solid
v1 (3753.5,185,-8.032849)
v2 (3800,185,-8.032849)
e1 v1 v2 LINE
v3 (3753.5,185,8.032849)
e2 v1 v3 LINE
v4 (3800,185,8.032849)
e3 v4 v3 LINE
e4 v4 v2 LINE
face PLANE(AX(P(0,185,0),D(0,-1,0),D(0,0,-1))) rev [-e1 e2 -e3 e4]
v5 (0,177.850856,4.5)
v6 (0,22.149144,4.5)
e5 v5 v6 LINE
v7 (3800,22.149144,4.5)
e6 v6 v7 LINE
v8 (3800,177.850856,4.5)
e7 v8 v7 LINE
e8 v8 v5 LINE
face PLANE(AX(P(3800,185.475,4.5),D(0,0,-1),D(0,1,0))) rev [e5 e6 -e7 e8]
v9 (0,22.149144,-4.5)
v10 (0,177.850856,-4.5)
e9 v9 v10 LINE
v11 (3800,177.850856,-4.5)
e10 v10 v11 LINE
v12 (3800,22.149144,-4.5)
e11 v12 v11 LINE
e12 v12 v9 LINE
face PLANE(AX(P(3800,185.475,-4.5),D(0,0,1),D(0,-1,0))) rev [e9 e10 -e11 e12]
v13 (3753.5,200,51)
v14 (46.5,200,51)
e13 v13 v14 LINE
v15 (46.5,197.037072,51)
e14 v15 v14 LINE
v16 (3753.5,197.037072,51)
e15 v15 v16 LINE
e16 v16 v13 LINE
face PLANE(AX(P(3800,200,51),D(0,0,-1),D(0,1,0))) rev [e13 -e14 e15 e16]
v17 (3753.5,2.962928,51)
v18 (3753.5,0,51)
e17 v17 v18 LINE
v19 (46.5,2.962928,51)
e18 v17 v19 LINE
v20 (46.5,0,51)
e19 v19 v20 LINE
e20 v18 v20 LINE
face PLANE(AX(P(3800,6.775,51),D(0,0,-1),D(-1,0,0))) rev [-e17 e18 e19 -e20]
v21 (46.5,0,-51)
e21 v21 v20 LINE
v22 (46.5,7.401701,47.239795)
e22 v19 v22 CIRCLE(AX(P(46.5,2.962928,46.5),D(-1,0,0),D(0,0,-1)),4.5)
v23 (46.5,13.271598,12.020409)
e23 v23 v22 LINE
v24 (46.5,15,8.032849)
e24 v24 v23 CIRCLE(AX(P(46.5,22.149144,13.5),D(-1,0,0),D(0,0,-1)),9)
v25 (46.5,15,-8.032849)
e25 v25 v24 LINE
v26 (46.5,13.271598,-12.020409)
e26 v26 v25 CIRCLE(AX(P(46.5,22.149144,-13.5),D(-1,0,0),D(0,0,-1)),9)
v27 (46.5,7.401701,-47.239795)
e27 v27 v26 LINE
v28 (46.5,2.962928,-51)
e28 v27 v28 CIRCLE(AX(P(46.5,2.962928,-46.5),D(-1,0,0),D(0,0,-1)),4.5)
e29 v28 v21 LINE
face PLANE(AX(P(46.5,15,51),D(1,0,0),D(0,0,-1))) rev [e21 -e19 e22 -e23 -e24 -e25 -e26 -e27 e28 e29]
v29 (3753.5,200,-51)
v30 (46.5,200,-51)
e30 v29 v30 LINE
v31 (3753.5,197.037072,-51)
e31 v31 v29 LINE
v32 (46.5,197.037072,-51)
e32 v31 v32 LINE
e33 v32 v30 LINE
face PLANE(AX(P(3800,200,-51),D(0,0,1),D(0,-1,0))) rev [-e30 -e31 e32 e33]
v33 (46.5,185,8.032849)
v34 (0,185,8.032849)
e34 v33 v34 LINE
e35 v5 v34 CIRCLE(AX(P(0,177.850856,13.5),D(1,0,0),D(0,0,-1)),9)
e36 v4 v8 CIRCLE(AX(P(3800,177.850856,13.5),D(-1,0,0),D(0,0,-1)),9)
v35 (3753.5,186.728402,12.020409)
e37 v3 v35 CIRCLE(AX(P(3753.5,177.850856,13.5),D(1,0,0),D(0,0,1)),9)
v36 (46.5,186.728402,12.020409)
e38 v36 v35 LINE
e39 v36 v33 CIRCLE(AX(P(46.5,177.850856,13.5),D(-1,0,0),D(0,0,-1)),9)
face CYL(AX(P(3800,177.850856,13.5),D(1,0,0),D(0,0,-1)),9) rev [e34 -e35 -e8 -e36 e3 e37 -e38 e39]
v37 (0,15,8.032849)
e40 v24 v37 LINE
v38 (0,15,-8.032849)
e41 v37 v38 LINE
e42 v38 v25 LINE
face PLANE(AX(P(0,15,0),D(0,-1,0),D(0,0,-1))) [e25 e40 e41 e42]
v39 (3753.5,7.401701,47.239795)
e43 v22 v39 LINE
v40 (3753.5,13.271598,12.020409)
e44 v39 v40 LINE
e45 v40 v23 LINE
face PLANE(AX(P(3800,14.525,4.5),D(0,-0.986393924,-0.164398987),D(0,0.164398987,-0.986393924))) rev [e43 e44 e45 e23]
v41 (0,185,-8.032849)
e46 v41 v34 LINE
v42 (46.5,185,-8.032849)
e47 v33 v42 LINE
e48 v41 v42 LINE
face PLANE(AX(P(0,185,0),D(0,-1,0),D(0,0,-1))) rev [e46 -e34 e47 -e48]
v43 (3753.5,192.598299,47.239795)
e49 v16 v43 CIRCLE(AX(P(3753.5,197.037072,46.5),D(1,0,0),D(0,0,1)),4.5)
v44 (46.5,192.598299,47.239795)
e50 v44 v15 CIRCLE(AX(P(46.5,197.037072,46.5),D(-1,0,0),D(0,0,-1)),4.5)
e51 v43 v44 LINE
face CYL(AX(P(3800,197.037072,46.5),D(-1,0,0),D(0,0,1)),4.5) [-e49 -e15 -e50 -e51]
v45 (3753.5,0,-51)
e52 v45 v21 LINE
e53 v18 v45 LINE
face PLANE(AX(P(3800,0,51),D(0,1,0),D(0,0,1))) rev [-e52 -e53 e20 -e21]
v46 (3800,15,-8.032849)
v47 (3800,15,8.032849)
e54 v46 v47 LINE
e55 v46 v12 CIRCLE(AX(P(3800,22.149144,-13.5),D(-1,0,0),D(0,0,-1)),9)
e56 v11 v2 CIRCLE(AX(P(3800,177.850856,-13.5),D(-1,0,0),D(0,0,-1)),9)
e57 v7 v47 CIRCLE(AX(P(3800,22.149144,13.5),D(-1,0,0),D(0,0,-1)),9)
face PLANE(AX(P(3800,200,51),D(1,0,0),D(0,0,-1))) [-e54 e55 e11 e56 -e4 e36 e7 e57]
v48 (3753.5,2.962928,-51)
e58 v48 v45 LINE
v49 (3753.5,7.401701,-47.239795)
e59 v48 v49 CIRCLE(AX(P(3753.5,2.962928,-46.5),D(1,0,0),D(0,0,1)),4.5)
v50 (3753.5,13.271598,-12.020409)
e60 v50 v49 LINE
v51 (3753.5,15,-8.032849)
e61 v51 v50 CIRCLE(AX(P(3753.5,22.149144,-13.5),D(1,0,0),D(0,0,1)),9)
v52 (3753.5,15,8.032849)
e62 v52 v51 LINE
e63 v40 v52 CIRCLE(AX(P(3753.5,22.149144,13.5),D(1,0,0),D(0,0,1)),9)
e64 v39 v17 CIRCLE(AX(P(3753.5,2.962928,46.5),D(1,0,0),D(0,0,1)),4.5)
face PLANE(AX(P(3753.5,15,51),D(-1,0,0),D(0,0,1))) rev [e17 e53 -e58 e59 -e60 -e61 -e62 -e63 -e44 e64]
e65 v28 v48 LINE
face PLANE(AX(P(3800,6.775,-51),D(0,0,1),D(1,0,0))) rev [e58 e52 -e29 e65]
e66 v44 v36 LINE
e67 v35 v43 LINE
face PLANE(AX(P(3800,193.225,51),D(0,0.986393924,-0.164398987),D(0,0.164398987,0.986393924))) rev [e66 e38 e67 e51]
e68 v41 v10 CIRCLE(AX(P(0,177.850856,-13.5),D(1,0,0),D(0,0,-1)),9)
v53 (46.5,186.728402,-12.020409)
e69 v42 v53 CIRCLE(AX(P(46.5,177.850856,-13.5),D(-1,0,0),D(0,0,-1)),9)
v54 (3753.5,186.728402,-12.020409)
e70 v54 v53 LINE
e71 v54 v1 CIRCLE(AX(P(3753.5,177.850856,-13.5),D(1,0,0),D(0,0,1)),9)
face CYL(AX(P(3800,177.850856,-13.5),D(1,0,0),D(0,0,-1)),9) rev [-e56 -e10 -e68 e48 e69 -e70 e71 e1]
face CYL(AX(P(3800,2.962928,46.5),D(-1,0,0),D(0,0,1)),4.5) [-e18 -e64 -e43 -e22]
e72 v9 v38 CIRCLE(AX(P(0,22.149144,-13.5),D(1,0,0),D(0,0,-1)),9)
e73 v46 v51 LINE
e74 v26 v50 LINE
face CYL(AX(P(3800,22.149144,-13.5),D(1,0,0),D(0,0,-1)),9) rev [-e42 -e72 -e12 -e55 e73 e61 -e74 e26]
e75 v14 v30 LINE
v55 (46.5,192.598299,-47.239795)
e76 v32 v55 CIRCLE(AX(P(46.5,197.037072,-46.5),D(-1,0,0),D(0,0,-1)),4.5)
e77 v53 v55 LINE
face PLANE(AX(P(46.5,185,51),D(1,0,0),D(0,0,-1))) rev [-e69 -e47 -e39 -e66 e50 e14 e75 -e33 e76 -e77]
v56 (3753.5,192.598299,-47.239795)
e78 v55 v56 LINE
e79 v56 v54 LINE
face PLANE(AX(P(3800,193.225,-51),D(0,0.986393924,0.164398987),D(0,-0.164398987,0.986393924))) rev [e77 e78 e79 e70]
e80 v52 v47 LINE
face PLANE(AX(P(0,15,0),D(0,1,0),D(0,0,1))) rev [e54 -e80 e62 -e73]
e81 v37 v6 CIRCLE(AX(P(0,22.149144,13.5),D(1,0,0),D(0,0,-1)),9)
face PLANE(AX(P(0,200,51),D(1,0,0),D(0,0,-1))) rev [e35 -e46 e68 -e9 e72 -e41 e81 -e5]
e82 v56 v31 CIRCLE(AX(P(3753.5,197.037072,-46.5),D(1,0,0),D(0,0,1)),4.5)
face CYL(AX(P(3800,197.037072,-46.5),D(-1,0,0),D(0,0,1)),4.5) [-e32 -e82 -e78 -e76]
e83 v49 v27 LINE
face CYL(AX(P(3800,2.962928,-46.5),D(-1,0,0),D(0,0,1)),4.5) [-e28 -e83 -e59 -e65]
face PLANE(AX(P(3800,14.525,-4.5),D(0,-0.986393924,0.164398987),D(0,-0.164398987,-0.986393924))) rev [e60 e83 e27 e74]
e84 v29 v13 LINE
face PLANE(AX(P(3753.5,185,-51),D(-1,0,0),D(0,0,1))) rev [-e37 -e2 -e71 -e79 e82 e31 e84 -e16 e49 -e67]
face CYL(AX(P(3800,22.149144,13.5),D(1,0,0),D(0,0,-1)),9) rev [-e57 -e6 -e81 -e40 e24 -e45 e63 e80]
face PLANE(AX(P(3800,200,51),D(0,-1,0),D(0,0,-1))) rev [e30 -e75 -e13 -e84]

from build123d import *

# Parameters (mm, degrees)
BASE_DEPTH         = 3800
FILLET1_R          = 9
FILLET2_R          = 4.5
SKETCH_1_W         = 46.5
SKETCH_1_H         = 102
CUT_EXTRUDE1_DEPTH = 15
SKETCH2_W          = 46.5
SKETCH2_H          = 102
CUT_EXTRUDE2_DEPTH = 15


with BuildPart() as part:
    # Sketch1 → Base (new body)
    with BuildSketch(Plane(origin=(0, 0, 0), x_dir=(0, 0, -1), z_dir=(1, 0, 0))):
        Polygon((-51, 0), (51, 0), (51, 6.775), (4.5, 14.525), (4.5, 185.475), (51, 193.225), (51, 200), (-51, 200), (-51, 193.225), (-4.5, 185.475), (-4.5, 14.525), (-51, 6.775), align=None)
    extrude(amount=BASE_DEPTH)

    # Fillet1
    fillet1_edges = [part.edges().sort_by_distance(p)[0] for p in [
        (1900, 14.525, 4.5),
        (1900, 185.475, 4.5),
        (1900, 185.475, -4.5),
        (1900, 14.525, -4.5),
    ]]
    fillet(fillet1_edges, radius=FILLET1_R)

    # Fillet2
    fillet2_edges = [part.edges().sort_by_distance(p)[0] for p in [
        (1900, 6.775, 51),
        (1900, 193.225, 51),
        (1900, 193.225, -51),
        (1900, 6.775, -51),
    ]]
    fillet(fillet2_edges, radius=FILLET2_R)

    # 草图1 → Cut-Extrude1 (cut)
    with BuildSketch(Plane(origin=(0, 200, 0), x_dir=(1, 0, 0), z_dir=(0, 1, 0))):
        with Locations((23.25, 0)):
            Rectangle(SKETCH_1_W, SKETCH_1_H)
        with Locations((3776.75, 0)):
            Rectangle(SKETCH_1_W, SKETCH_1_H)
    extrude(amount=-CUT_EXTRUDE1_DEPTH, mode=Mode.SUBTRACT)

    # Sketch2 → Cut-Extrude2 (cut)
    with BuildSketch(Plane(origin=(0, 0, 0), x_dir=(-1, 0, 0), z_dir=(0, -1, 0))):
        with Locations((-23.25, 0)):
            Rectangle(SKETCH2_W, SKETCH2_H)
        with Locations((-3776.75, 0)):
            Rectangle(SKETCH2_W, SKETCH2_H)
    extrude(amount=-CUT_EXTRUDE2_DEPTH, mode=Mode.SUBTRACT)


solid = part.part
